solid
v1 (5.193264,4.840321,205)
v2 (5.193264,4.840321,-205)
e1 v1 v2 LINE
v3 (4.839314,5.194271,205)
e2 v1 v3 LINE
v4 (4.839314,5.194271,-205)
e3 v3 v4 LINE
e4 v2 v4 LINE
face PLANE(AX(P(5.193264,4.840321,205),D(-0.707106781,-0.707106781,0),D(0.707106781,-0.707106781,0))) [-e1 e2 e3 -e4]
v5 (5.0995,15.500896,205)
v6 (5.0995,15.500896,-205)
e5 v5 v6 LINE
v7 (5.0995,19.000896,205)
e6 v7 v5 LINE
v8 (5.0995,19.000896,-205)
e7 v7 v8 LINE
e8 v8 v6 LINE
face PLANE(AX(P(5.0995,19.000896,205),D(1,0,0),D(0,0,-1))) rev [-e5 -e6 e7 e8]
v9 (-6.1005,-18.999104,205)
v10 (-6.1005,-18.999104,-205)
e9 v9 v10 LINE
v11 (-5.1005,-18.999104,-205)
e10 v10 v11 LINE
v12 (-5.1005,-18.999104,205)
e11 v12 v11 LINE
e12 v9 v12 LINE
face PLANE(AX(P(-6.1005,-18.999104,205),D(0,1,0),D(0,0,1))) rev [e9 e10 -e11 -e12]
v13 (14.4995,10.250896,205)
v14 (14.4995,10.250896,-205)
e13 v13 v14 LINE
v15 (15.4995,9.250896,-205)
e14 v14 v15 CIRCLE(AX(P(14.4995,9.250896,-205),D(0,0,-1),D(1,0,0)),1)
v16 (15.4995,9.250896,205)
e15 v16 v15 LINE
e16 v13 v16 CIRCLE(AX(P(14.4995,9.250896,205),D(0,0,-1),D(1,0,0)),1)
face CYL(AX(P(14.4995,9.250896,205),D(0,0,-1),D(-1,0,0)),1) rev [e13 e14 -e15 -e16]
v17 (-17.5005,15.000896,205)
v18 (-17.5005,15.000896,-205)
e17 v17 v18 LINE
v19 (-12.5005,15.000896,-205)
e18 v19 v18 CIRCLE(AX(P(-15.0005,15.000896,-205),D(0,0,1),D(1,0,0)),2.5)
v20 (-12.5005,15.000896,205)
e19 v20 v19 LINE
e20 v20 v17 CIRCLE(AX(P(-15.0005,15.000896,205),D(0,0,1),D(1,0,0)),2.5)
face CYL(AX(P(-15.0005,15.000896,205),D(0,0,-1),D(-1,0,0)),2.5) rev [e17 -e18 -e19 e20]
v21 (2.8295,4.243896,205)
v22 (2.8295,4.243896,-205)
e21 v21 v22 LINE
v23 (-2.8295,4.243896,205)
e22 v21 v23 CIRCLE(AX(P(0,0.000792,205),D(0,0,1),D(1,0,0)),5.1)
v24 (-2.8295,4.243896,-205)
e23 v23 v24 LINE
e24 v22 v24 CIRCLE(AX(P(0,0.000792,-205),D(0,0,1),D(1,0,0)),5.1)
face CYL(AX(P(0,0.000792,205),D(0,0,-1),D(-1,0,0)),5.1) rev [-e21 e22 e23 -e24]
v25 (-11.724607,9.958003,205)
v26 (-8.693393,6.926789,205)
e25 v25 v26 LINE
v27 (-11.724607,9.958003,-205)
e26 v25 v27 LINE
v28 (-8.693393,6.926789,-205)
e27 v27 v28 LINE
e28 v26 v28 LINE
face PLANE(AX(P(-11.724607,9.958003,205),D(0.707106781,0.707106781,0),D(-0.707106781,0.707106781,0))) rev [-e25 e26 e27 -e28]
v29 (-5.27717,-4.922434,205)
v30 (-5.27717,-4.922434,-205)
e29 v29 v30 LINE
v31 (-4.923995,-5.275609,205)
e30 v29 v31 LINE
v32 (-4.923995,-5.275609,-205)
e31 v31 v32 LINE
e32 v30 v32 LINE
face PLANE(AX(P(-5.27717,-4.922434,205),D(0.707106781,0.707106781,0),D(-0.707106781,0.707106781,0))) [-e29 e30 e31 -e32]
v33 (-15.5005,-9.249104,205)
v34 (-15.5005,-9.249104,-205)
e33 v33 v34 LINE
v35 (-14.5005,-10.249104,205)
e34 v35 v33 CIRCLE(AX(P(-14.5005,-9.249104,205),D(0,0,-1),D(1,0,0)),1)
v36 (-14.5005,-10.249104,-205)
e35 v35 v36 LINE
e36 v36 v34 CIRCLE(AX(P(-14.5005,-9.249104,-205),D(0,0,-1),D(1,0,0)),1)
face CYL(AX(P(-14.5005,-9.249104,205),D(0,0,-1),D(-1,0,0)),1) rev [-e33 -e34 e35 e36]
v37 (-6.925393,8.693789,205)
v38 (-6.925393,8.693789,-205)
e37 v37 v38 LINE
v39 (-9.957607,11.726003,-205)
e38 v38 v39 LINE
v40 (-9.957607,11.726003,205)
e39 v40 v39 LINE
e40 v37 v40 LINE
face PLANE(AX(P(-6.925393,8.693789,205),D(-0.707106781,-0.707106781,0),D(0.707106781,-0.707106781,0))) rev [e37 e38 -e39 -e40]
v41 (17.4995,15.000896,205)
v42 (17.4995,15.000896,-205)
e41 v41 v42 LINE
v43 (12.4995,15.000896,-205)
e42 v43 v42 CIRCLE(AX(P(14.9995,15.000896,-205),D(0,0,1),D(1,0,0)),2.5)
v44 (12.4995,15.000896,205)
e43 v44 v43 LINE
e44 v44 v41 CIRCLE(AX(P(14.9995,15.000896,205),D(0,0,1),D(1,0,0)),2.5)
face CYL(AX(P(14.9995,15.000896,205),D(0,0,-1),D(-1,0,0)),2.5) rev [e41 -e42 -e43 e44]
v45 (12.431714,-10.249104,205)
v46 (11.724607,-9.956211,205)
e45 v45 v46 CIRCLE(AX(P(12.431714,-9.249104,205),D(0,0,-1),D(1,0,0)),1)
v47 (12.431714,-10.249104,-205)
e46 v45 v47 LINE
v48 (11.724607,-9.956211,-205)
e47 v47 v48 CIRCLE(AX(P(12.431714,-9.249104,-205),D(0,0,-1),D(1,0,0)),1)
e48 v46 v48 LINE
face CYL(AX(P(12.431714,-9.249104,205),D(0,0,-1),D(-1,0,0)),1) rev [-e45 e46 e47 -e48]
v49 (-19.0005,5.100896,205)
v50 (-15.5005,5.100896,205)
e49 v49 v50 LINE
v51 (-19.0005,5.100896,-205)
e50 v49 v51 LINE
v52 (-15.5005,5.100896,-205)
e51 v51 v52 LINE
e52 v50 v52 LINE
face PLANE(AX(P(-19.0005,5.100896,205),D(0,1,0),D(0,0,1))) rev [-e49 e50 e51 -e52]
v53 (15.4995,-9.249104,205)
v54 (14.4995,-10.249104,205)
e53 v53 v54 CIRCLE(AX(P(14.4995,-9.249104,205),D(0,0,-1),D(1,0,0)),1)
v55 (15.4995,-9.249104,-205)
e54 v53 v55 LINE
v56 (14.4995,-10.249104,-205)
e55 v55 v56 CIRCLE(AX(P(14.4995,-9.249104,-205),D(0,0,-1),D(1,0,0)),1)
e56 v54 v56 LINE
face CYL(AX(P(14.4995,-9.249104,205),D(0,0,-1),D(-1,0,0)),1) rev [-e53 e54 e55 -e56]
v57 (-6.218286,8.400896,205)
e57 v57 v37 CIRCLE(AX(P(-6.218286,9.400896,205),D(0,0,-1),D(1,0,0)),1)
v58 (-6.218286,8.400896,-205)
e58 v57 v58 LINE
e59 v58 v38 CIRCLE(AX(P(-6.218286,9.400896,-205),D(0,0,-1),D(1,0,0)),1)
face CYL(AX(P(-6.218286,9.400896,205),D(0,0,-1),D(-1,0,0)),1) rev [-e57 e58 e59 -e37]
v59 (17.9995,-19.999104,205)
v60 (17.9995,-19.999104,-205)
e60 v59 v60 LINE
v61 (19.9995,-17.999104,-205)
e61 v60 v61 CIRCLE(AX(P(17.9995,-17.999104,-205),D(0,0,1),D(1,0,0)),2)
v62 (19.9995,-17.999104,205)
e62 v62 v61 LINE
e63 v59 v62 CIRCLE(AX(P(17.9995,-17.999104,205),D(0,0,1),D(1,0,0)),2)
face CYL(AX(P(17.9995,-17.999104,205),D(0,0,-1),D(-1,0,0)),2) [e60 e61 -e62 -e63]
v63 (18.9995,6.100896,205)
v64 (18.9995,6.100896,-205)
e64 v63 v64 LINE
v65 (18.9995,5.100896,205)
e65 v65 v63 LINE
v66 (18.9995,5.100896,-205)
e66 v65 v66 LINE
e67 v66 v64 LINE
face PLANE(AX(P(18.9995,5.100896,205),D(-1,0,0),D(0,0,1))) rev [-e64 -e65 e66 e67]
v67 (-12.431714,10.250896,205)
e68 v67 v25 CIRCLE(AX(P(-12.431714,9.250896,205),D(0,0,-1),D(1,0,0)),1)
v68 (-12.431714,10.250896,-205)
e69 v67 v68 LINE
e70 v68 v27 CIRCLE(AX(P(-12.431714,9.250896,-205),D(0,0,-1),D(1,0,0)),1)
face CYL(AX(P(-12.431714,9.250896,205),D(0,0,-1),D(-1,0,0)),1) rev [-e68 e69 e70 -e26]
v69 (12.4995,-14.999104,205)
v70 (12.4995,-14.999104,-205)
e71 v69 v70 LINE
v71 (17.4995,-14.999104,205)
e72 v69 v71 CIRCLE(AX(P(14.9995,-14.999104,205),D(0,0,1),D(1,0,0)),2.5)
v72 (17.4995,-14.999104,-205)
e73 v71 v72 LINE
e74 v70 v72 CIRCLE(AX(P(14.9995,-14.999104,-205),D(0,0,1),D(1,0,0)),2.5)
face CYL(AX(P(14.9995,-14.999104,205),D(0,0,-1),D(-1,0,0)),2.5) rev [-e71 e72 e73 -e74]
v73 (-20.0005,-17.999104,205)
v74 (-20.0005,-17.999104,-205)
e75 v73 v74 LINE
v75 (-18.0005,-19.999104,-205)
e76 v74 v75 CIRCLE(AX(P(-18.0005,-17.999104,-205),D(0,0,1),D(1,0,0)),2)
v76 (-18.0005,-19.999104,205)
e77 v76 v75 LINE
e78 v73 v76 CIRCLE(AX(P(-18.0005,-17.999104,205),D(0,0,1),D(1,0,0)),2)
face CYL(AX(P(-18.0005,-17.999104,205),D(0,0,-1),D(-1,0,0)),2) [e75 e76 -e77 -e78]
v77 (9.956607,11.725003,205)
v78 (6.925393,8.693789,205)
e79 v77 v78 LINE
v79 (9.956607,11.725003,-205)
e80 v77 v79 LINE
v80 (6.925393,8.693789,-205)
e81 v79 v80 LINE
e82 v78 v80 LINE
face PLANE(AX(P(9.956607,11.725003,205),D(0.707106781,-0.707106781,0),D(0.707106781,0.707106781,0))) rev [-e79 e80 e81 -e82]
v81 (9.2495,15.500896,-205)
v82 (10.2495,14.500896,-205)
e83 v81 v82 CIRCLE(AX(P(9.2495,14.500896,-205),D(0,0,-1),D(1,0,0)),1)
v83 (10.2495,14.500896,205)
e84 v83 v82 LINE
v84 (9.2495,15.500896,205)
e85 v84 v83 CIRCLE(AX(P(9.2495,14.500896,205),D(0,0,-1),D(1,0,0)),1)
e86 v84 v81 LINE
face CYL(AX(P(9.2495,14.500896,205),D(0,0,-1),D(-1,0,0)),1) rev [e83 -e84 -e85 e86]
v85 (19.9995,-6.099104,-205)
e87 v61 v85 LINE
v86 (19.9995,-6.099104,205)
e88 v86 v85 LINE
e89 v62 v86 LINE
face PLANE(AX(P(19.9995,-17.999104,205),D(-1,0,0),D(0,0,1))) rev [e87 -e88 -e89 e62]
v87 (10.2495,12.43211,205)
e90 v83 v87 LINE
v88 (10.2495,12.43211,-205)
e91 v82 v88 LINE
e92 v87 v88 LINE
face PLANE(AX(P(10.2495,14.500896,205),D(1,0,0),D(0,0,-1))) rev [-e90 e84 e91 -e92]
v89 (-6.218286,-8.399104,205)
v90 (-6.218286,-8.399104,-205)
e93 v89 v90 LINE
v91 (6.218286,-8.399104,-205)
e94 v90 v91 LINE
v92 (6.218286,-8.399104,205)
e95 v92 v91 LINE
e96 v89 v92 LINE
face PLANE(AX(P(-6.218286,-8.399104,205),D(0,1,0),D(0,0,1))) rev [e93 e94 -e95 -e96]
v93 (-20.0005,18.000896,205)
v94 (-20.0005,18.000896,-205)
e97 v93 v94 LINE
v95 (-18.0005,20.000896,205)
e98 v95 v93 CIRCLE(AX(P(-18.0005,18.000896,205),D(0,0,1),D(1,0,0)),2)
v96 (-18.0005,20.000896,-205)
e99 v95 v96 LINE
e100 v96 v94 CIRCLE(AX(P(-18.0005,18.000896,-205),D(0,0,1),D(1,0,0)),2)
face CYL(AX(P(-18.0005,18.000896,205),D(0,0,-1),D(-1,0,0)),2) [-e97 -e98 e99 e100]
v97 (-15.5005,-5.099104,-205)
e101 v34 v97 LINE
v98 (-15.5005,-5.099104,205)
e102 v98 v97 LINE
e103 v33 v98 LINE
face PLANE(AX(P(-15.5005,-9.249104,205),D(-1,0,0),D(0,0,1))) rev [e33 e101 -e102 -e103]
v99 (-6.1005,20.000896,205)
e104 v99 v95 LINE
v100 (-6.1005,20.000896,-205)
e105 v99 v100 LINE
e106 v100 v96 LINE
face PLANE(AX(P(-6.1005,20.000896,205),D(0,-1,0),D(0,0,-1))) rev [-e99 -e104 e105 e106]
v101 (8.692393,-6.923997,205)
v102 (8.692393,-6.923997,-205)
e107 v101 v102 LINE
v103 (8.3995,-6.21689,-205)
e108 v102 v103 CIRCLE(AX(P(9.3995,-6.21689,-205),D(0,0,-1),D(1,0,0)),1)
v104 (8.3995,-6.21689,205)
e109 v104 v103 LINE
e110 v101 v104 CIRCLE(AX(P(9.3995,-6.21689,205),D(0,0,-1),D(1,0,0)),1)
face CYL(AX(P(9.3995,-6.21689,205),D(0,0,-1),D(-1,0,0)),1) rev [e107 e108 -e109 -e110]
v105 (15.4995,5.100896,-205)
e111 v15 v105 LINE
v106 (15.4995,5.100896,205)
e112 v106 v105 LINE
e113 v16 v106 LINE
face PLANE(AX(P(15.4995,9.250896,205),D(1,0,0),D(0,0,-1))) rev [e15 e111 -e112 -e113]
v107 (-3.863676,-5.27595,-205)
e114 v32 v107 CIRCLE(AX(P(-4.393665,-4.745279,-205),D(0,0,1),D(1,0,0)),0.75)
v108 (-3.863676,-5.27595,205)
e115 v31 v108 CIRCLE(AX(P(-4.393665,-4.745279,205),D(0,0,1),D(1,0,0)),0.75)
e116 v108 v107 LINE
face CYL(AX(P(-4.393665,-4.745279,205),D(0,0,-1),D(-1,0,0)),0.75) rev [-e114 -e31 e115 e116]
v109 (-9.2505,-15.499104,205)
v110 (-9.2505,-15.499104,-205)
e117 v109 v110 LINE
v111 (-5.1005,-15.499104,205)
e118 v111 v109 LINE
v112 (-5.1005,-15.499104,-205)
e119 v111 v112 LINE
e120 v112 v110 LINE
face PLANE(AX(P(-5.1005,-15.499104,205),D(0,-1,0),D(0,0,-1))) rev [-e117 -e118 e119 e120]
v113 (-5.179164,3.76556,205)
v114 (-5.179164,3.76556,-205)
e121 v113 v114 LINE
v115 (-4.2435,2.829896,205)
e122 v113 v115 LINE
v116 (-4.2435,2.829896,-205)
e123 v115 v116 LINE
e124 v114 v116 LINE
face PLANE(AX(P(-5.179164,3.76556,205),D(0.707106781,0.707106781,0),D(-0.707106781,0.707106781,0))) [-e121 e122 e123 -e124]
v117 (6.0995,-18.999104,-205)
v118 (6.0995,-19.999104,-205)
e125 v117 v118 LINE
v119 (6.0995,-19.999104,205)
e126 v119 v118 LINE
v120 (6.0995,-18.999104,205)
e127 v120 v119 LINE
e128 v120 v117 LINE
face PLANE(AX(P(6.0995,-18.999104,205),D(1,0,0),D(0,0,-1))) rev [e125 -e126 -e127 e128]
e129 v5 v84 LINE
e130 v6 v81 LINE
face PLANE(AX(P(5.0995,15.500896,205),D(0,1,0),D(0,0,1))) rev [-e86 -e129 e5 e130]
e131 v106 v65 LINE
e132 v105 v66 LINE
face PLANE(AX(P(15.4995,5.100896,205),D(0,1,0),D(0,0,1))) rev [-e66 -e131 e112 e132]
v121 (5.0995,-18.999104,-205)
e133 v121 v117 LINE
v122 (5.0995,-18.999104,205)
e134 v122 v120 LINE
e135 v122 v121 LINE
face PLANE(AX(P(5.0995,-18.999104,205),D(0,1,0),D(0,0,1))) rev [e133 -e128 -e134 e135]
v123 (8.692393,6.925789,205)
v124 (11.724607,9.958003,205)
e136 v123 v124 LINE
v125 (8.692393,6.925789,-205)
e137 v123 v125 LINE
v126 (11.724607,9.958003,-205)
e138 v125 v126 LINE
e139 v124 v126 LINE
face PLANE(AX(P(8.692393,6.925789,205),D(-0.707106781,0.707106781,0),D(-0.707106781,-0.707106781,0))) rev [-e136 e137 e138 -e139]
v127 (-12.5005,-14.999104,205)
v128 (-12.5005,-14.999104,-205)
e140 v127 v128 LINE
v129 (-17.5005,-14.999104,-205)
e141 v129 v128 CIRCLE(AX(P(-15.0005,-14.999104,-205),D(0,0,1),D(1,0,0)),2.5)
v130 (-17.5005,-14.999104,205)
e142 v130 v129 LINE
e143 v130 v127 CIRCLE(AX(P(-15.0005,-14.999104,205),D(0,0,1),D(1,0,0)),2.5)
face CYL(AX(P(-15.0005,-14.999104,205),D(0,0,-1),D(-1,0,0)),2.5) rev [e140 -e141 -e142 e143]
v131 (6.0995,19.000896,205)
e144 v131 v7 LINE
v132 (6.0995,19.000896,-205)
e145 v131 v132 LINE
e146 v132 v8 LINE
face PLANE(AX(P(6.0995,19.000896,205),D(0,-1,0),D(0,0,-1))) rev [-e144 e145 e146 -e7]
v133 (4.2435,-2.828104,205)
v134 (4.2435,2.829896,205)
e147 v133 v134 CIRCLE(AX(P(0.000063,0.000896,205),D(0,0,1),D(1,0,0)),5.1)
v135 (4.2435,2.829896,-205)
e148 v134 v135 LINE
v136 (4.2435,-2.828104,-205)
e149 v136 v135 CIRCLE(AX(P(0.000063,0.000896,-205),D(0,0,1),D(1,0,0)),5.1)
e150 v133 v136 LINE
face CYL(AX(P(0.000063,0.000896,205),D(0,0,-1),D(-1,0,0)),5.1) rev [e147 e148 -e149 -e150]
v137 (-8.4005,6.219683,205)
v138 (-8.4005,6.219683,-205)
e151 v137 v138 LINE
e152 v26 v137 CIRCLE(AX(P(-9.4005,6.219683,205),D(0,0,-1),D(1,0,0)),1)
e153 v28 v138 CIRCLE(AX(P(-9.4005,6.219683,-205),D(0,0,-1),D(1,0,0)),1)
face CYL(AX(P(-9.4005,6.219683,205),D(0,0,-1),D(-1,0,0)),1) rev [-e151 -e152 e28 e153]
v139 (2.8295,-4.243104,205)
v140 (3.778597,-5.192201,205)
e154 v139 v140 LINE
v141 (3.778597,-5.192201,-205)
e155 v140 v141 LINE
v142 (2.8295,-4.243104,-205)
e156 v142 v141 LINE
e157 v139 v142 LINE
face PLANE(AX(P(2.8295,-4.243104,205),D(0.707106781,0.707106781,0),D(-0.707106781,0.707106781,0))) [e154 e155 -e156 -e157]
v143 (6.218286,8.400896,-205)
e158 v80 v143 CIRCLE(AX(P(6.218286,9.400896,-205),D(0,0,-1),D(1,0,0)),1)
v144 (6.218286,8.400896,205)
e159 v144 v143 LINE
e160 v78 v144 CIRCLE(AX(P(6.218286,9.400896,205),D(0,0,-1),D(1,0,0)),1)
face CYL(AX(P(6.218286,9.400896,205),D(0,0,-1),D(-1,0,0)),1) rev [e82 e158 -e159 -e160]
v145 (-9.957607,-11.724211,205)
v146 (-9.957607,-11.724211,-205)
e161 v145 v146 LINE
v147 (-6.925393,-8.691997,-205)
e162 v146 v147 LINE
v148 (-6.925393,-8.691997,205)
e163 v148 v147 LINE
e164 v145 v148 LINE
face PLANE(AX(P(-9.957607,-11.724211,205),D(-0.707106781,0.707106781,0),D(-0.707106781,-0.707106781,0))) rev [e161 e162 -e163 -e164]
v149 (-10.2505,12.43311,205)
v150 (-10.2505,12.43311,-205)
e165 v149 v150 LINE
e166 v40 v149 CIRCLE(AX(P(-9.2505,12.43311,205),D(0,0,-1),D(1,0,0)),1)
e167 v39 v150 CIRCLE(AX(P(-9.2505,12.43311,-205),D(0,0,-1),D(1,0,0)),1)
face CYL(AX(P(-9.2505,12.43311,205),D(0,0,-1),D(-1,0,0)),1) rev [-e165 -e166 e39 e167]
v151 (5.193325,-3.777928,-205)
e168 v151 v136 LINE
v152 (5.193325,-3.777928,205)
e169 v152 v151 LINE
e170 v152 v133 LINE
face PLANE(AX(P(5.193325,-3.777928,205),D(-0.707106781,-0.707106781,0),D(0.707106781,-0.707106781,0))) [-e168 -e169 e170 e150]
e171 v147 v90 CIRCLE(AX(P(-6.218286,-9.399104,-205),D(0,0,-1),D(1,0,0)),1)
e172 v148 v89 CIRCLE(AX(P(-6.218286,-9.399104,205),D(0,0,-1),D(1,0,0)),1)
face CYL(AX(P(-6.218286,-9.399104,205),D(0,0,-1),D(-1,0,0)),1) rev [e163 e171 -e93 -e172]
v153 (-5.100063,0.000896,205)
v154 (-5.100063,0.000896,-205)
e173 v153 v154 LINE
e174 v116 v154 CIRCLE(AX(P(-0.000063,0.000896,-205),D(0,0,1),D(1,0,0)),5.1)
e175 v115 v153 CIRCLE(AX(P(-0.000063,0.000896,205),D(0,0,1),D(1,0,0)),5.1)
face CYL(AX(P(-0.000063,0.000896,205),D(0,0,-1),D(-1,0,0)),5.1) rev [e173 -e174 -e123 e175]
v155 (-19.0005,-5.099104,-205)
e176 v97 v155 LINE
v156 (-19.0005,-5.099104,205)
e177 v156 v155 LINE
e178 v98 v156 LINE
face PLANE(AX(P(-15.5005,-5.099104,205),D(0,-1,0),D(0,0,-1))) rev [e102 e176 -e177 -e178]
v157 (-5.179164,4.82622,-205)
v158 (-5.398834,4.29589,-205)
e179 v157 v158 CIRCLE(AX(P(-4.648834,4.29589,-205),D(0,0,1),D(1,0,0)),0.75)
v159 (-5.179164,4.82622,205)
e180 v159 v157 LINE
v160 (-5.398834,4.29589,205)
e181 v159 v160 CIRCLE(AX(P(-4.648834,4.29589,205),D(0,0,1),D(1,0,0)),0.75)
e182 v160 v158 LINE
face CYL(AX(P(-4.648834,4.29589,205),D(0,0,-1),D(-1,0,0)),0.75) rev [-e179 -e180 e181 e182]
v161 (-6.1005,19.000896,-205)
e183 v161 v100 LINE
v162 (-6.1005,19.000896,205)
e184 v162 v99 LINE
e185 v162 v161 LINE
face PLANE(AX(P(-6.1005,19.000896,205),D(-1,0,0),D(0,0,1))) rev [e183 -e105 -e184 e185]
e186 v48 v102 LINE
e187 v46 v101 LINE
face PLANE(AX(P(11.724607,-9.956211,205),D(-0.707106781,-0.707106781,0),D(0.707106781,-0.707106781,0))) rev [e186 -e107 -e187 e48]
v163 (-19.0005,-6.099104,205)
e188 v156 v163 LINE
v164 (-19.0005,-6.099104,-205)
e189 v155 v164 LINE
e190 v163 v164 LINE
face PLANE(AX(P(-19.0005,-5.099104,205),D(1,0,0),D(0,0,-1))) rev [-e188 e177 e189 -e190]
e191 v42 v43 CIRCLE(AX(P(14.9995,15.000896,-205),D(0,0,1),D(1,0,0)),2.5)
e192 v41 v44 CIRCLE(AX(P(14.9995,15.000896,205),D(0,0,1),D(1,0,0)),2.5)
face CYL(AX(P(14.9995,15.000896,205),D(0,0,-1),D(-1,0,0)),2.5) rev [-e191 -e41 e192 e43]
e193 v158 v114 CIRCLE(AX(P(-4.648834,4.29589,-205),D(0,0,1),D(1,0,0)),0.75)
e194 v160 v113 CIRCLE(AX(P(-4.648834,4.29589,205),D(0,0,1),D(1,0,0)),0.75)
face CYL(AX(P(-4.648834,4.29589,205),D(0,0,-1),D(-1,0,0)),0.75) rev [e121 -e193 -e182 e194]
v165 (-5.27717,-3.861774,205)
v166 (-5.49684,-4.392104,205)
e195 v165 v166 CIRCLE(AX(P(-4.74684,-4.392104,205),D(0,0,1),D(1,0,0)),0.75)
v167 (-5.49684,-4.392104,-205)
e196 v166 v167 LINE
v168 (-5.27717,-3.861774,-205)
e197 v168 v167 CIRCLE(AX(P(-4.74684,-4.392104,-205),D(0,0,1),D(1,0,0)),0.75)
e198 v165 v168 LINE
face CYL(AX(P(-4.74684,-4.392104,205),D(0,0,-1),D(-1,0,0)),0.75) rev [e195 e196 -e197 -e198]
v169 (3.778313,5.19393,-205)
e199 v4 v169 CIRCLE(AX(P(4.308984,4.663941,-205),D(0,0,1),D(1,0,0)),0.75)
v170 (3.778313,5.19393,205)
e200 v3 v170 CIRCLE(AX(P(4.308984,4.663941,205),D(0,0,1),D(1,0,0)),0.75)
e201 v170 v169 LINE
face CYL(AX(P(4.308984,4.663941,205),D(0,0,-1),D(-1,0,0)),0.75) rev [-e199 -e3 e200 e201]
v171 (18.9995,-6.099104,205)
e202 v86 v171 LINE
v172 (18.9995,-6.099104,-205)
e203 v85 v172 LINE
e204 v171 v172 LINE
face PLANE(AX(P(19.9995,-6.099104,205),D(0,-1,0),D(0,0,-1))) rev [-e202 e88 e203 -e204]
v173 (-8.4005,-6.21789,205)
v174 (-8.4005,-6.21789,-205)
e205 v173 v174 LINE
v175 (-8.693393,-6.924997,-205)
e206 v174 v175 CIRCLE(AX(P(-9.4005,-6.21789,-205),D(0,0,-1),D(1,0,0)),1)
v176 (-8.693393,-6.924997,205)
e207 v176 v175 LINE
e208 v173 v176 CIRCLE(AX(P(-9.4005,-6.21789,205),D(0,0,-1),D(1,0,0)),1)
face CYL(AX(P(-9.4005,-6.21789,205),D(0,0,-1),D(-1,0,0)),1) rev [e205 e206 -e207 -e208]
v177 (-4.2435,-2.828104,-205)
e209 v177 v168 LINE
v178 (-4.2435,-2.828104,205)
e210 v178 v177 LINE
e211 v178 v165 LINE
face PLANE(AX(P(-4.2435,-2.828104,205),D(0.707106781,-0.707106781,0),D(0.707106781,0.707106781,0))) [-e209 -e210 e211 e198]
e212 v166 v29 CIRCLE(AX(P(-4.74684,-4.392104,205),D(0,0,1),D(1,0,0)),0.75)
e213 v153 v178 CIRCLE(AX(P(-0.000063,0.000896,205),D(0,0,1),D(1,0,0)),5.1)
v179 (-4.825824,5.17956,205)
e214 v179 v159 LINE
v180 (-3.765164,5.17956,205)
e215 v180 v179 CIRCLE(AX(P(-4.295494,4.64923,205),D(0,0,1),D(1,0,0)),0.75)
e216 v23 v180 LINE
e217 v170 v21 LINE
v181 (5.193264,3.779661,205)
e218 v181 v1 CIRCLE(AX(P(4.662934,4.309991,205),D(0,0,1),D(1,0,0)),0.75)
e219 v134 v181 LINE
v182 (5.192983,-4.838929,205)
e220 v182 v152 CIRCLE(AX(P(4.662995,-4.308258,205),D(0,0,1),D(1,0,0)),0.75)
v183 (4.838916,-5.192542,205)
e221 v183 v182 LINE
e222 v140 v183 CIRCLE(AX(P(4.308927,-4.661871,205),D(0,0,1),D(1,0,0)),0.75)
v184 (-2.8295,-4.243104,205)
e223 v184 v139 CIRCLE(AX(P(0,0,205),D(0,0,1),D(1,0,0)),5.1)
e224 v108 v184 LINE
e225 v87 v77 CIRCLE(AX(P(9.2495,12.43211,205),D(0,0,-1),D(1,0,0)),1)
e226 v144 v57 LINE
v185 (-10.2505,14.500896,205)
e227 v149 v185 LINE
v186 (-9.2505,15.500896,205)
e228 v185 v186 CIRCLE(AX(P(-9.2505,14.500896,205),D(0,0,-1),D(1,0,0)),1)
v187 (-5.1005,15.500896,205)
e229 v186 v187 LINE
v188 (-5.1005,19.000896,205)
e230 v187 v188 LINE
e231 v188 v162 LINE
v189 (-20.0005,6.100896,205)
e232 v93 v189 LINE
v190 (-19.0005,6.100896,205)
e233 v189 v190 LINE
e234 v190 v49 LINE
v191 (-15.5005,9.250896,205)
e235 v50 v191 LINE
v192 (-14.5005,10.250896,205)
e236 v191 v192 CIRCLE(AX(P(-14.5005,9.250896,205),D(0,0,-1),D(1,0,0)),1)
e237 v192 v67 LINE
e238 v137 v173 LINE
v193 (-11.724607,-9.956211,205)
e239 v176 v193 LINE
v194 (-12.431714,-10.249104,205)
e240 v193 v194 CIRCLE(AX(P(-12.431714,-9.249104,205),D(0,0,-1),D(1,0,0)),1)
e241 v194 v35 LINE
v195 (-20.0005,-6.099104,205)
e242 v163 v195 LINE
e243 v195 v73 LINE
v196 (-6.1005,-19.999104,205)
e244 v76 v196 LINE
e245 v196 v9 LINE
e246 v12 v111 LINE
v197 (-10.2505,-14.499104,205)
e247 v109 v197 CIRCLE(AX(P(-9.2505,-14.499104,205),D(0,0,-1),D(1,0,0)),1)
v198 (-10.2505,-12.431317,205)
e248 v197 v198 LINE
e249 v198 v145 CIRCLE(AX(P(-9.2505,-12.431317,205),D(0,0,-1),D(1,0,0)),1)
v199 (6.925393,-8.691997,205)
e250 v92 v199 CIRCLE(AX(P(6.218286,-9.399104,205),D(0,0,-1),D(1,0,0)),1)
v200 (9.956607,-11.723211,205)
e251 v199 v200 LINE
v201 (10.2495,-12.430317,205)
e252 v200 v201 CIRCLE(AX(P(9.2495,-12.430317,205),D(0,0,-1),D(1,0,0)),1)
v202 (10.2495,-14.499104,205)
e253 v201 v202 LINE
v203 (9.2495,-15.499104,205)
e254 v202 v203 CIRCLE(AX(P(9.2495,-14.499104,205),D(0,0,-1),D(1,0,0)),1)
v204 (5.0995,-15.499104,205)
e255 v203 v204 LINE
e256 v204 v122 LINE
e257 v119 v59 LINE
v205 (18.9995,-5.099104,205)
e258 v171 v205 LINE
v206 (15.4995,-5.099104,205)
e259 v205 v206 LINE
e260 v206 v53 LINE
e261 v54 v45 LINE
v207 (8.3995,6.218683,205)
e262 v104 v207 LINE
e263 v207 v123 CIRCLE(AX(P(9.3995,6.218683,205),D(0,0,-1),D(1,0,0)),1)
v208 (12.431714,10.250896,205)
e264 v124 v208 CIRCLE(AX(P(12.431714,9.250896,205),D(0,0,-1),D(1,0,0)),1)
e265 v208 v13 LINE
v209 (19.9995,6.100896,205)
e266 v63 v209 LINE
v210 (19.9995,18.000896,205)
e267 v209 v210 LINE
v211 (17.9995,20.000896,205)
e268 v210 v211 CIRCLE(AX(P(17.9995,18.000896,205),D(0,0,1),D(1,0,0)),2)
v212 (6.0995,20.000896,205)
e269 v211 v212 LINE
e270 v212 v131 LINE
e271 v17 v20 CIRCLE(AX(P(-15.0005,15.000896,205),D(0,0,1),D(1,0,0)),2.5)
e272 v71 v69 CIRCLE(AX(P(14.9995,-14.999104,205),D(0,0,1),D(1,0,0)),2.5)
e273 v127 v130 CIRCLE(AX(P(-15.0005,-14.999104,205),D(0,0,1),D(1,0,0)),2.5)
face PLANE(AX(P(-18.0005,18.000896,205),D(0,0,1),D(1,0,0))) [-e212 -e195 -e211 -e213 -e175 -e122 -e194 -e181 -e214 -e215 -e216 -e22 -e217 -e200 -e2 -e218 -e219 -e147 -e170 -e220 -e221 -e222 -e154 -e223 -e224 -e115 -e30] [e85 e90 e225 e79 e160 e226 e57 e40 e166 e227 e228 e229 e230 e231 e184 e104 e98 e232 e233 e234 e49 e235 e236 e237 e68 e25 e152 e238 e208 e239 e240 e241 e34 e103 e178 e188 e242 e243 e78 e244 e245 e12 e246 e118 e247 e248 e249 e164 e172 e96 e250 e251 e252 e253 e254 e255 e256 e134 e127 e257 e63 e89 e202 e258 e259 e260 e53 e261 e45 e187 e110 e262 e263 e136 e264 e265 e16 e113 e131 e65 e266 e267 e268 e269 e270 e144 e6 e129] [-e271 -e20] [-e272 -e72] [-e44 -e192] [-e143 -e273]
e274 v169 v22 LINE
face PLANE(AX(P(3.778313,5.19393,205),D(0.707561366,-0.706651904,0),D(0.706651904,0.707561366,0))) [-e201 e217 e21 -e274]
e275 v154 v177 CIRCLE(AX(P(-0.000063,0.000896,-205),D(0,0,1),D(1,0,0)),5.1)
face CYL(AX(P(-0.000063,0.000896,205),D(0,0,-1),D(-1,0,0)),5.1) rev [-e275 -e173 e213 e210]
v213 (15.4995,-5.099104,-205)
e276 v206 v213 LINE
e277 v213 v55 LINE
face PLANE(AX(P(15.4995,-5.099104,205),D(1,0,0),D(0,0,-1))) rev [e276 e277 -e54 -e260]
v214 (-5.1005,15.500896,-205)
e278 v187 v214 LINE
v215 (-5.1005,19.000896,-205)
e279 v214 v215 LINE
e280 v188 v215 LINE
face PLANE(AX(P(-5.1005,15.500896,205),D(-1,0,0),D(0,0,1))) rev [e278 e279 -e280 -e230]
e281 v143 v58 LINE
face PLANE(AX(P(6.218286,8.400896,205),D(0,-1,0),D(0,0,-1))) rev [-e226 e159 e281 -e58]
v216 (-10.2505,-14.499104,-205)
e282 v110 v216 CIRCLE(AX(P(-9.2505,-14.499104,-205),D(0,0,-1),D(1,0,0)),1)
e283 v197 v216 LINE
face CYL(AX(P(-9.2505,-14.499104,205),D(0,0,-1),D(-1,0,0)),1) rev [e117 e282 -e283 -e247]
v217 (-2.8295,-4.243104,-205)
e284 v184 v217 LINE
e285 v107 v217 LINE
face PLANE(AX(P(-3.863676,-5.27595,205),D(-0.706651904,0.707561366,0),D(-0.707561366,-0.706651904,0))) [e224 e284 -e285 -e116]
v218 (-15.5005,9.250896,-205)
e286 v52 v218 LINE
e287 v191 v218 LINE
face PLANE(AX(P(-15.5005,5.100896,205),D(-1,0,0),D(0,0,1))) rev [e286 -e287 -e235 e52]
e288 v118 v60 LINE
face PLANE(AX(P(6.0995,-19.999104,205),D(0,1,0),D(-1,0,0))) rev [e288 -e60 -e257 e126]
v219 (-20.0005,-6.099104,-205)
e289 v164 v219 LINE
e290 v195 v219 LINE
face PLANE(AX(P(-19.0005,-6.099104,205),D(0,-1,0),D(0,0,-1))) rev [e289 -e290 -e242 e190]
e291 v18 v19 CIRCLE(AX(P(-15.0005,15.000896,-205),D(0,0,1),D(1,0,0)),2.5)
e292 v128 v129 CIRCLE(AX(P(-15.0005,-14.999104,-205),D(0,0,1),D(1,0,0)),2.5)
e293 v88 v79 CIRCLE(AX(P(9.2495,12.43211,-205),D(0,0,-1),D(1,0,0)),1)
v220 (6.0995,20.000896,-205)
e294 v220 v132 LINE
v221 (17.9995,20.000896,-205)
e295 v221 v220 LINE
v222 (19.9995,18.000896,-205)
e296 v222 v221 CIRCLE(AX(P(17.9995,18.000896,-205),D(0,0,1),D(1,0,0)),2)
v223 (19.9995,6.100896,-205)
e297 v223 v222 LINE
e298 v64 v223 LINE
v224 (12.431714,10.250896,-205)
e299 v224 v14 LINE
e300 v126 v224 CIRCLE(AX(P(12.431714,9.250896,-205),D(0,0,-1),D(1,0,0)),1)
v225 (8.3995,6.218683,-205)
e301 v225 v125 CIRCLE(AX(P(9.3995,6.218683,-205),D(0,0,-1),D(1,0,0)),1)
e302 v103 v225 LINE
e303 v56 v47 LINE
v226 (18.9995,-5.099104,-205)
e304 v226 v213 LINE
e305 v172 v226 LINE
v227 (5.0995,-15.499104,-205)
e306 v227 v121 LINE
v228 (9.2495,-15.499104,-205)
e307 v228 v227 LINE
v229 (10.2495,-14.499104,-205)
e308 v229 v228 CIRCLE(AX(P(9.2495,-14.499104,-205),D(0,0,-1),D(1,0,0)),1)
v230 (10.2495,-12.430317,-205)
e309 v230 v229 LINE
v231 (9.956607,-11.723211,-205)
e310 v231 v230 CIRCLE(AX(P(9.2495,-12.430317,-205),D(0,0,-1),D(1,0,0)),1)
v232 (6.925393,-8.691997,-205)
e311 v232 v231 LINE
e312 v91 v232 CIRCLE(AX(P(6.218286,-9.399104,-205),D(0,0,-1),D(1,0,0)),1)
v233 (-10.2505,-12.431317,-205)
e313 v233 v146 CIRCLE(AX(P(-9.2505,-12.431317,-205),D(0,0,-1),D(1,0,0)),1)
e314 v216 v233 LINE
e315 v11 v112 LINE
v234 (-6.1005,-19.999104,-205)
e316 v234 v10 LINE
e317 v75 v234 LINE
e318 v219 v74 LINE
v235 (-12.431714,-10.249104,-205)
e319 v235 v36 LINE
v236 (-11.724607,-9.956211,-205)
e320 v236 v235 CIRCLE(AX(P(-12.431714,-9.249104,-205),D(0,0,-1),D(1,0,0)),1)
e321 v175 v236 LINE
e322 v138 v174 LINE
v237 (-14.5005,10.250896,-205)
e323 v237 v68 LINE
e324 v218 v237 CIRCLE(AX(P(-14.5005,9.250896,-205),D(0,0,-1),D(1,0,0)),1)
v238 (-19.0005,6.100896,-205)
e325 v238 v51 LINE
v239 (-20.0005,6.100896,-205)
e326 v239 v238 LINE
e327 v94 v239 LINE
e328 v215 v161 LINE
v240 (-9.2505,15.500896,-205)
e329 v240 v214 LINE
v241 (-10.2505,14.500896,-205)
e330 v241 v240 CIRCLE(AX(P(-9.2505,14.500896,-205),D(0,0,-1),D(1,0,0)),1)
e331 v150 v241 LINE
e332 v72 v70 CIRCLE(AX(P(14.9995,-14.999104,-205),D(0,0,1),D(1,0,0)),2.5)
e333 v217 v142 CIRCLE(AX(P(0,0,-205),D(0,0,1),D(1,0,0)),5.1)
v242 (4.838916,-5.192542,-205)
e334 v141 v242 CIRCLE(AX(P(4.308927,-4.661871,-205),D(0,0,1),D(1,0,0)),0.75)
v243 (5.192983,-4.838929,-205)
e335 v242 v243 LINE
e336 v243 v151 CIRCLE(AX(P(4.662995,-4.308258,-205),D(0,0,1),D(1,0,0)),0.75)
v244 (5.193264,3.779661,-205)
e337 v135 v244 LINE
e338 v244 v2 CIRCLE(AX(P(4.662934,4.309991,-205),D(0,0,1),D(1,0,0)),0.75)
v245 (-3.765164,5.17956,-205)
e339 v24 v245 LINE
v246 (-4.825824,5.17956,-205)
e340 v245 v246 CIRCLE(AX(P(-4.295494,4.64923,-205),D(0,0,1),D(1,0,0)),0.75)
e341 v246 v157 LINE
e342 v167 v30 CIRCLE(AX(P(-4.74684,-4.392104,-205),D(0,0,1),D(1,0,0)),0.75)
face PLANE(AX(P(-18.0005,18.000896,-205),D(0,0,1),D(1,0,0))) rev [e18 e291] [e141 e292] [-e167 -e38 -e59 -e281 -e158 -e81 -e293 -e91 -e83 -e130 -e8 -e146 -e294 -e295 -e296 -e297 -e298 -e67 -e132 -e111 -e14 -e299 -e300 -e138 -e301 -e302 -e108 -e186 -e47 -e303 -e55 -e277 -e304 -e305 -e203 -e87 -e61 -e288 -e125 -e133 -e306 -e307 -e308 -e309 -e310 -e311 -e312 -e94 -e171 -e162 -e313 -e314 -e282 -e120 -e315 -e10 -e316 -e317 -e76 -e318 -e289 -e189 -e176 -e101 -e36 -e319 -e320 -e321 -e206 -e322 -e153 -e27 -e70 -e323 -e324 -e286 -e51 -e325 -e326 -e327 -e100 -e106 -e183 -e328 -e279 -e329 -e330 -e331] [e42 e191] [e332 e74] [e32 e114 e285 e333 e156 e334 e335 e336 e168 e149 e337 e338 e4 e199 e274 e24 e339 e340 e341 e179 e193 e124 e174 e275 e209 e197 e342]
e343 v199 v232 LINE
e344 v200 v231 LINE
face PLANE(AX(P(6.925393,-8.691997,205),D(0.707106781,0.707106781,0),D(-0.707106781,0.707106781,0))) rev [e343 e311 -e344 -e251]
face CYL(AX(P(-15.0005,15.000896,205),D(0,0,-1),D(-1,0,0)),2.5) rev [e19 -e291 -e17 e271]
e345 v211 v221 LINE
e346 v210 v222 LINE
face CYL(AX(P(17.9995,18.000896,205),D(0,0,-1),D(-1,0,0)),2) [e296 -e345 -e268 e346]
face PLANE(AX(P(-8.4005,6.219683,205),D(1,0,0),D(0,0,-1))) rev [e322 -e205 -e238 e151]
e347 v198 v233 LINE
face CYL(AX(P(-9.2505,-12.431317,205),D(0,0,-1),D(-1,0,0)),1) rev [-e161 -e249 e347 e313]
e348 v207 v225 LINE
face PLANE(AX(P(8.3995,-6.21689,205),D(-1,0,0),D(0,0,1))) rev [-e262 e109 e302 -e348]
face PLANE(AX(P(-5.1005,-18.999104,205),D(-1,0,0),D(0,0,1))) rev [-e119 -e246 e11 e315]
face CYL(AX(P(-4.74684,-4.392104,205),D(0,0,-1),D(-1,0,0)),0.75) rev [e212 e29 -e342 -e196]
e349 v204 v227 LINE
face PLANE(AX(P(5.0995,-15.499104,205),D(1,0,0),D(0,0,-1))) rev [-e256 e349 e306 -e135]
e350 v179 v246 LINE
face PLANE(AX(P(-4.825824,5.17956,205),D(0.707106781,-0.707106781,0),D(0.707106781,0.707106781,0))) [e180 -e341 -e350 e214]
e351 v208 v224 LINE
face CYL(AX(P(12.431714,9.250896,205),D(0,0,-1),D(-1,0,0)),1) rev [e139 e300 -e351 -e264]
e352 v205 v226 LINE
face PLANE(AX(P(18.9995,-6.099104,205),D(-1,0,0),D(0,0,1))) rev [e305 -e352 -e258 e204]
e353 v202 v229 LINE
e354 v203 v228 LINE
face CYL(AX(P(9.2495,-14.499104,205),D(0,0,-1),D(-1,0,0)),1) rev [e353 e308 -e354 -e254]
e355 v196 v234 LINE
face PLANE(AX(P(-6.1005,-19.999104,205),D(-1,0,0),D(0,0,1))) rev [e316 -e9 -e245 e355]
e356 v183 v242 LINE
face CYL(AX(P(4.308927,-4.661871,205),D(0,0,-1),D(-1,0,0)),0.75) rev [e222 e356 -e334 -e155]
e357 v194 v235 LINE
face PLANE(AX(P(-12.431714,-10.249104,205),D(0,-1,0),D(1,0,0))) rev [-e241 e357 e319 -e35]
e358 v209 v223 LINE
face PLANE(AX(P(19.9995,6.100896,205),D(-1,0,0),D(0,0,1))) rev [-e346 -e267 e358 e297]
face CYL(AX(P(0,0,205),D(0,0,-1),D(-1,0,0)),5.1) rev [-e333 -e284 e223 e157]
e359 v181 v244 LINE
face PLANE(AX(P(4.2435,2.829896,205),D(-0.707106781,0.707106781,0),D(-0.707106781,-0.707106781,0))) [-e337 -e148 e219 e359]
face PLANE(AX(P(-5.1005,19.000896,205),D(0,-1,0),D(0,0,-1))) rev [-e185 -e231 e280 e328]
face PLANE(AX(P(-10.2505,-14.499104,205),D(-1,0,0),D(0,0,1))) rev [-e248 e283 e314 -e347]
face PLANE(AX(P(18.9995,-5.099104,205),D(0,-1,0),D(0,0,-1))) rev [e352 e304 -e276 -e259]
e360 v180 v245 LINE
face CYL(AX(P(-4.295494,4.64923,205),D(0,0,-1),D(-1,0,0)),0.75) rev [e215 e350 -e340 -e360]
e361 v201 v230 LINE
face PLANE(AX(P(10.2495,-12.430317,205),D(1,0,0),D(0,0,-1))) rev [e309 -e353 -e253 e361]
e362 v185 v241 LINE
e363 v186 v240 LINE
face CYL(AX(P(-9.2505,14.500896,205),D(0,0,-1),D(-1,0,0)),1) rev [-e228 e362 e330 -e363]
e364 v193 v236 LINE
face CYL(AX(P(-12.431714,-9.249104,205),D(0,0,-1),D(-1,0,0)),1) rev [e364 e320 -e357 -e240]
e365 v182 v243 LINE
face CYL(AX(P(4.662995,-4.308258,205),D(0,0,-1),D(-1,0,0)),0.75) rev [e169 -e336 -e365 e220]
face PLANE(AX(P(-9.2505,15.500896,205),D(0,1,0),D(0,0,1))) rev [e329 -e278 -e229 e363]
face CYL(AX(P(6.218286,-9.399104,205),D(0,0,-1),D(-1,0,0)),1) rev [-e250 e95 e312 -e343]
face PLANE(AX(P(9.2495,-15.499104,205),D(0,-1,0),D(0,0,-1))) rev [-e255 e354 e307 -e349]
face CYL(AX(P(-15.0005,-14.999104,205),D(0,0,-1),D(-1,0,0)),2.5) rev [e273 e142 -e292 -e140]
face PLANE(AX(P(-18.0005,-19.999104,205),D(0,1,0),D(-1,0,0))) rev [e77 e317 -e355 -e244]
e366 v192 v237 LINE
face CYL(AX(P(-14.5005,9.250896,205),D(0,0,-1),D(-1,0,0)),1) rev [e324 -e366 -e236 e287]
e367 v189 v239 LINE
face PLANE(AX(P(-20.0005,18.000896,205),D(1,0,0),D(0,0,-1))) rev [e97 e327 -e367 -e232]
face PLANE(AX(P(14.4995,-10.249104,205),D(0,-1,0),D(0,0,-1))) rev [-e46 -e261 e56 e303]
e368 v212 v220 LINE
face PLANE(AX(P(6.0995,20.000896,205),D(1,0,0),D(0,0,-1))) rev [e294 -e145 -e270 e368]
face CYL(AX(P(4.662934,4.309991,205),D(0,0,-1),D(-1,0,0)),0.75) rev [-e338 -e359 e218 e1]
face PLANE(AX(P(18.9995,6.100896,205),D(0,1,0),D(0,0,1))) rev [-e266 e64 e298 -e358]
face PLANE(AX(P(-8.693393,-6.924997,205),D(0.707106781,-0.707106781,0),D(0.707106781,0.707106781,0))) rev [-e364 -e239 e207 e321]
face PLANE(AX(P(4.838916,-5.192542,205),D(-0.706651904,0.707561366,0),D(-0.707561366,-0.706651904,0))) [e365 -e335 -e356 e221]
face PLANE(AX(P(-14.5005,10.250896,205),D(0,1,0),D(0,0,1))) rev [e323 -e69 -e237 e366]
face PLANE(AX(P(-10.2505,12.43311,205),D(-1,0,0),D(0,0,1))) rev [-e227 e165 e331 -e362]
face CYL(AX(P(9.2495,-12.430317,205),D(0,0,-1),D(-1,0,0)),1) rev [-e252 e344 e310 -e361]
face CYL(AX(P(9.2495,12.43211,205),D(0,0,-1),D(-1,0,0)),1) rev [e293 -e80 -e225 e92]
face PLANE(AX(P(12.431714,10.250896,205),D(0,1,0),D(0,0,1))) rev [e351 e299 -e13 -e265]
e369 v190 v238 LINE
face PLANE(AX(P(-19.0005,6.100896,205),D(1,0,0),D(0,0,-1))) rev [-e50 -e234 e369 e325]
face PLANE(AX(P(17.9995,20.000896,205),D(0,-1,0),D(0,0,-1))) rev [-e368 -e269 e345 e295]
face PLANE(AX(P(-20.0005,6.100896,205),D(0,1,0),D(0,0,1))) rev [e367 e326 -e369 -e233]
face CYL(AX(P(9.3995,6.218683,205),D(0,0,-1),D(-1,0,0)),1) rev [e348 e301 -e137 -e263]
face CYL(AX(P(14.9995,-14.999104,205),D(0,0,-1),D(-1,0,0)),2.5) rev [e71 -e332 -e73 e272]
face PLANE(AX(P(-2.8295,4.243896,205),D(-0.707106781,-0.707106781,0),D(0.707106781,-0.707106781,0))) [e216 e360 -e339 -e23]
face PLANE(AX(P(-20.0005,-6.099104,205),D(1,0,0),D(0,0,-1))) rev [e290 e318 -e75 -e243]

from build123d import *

# Parameters (mm, degrees)
SKETCH1_R           = 2.5
BOSS_EXTRUDE1_DEPTH = 205


with BuildPart() as part:
    # Sketch1 → Boss-Extrude1 (new, symmetric)
    with BuildSketch(Plane.XY):
        with BuildLine():
            Line((-5.1005, 15.500896213), (-5.1005, 19.000896213))
            Line((-5.1005, 19.000896213), (-6.1005, 19.000896213))
            Line((-6.1005, 19.000896213), (-6.1005, 20.000896213))
            Line((-6.1005, 20.000896213), (-18.0005, 20.000896213))
            ThreePointArc((-18.0005, 20.000896213), (-19.414713562, 19.415109775), (-20.0005, 18.000896213))
            Line((-20.0005, 18.000896213), (-20.0005, 6.100896213))
            Line((-20.0005, 6.100896213), (-19.0005, 6.100896213))
            Line((-19.0005, 6.100896213), (-19.0005, 5.100896213))
            Line((-19.0005, 5.100896213), (-15.5005, 5.100896213))
            Line((-15.5005, 5.100896213), (-15.5005, 9.250896213))
            ThreePointArc((-15.5005, 9.250896213), (-15.207606781, 9.958002994), (-14.5005, 10.250896213))
            Line((-14.5005, 10.250896213), (-12.431713562, 10.250896213))
            ThreePointArc((-12.431713562, 10.250896213), (-12.049030228, 10.174775786), (-11.724606932, 9.958003144))
            Line((-11.724606932, 9.958003144), (-8.693393219, 6.926789431))
            ThreePointArc((-8.693393219, 6.926789431), (-8.476620546, 6.602366272), (-8.4005, 6.21968306))
            Line((-8.4005, 6.21968306), (-8.4005, -6.217890225))
            ThreePointArc((-8.4005, -6.217890225), (-8.476620502, -6.60057374), (-8.693393346, -6.924997133))
            Line((-8.693393346, -6.924997133), (-11.724606781, -9.956210569))
            ThreePointArc((-11.724606781, -9.956210569), (-12.049030198, -10.172983348), (-12.431713709, -10.249103787))
            Line((-12.431713709, -10.249103787), (-14.5005, -10.249103787))
            ThreePointArc((-14.5005, -10.249103787), (-15.207606781, -9.956210569), (-15.5005, -9.249103787))
            Line((-15.5005, -9.249103787), (-15.5005, -5.099103787))
            Line((-15.5005, -5.099103787), (-19.0005, -5.099103787))
            Line((-19.0005, -5.099103787), (-19.0005, -6.099103787))
            Line((-19.0005, -6.099103787), (-20.0005, -6.099103787))
            Line((-20.0005, -6.099103787), (-20.0005, -17.999103787))
            ThreePointArc((-20.0005, -17.999103787), (-19.414713562, -19.41331735), (-18.0005, -19.999103787))
            Line((-18.0005, -19.999103787), (-6.1005, -19.999103787))
            Line((-6.1005, -19.999103787), (-6.1005, -18.999103787))
            Line((-6.1005, -18.999103787), (-5.1005, -18.999103787))
            Line((-5.1005, -18.999103787), (-5.1005, -15.499103787))
            Line((-5.1005, -15.499103787), (-9.2505, -15.499103787))
            ThreePointArc((-9.2505, -15.499103787), (-9.957606781, -15.206210569), (-10.2505, -14.499103787))
            Line((-10.2505, -14.499103787), (-10.2505, -12.43131735))
            ThreePointArc((-10.2505, -12.43131735), (-10.174379535, -12.048633922), (-9.957606789, -11.724210576))
            Line((-9.957606789, -11.724210576), (-6.925393219, -8.691997006))
            ThreePointArc((-6.925393219, -8.691997006), (-6.60096987, -8.475224255), (-6.218286438, -8.399103787))
            Line((-6.218286438, -8.399103787), (6.218286438, -8.399103787))
            ThreePointArc((6.218286438, -8.399103787), (6.600969772, -8.475224214), (6.925393068, -8.691996856))
            Line((6.925393068, -8.691996856), (9.956606781, -11.723210569))
            ThreePointArc((9.956606781, -11.723210569), (10.173379454, -12.047633728), (10.2495, -12.43031694))
            Line((10.2495, -12.43031694), (10.2495, -14.499103787))
            ThreePointArc((10.2495, -14.499103787), (9.956606781, -15.206210569), (9.2495, -15.499103787))
            Line((9.2495, -15.499103787), (5.0995, -15.499103787))
            Line((5.0995, -15.499103787), (5.0995, -18.999103787))
            Line((5.0995, -18.999103787), (6.0995, -18.999103787))
            Line((6.0995, -18.999103787), (6.0995, -19.999103787))
            Line((6.0995, -19.999103787), (17.9995, -19.999103787))
            ThreePointArc((17.9995, -19.999103787), (19.413713562, -19.41331735), (19.9995, -17.999103787))
            Line((19.9995, -17.999103787), (19.9995, -6.099103787))
            Line((19.9995, -6.099103787), (18.9995, -6.099103787))
            Line((18.9995, -6.099103787), (18.9995, -5.099103787))
            Line((18.9995, -5.099103787), (15.4995, -5.099103787))
            Line((15.4995, -5.099103787), (15.4995, -9.249103787))
            ThreePointArc((15.4995, -9.249103787), (15.206606781, -9.956210569), (14.4995, -10.249103787))
            Line((14.4995, -10.249103787), (12.431713562, -10.249103787))
            ThreePointArc((12.431713562, -10.249103787), (12.049030135, -10.172983322), (11.724606789, -9.956210576))
            Line((11.724606789, -9.956210576), (8.692393219, -6.923997006))
            ThreePointArc((8.692393219, -6.923997006), (8.475620467, -6.599573657), (8.3995, -6.216890225))
            Line((8.3995, -6.216890225), (8.3995, 6.21868265))
            ThreePointArc((8.3995, 6.21868265), (8.475620465, 6.601366078), (8.692393211, 6.925789424))
            Line((8.692393211, 6.925789424), (11.724606781, 9.958002994))
            ThreePointArc((11.724606781, 9.958002994), (12.04903013, 10.174775745), (12.431713562, 10.250896213))
            Line((12.431713562, 10.250896213), (14.4995, 10.250896213))
            ThreePointArc((14.4995, 10.250896213), (15.206606781, 9.958002994), (15.4995, 9.250896213))
            Line((15.4995, 9.250896213), (15.4995, 5.100896213))
            Line((15.4995, 5.100896213), (18.9995, 5.100896213))
            Line((18.9995, 5.100896213), (18.9995, 6.100896213))
            Line((18.9995, 6.100896213), (19.9995, 6.100896213))
            Line((19.9995, 6.100896213), (19.9995, 18.000896213))
            ThreePointArc((19.9995, 18.000896213), (19.413713562, 19.415109775), (17.9995, 20.000896213))
            Line((17.9995, 20.000896213), (6.0995, 20.000896213))
            Line((6.0995, 20.000896213), (6.0995, 19.000896213))
            Line((6.0995, 19.000896213), (5.0995, 19.000896213))
            Line((5.0995, 19.000896213), (5.0995, 15.500896213))
            Line((5.0995, 15.500896213), (9.2495, 15.500896213))
            ThreePointArc((9.2495, 15.500896213), (9.956606781, 15.208002994), (10.2495, 14.500896213))
            Line((10.2495, 14.500896213), (10.2495, 12.432109775))
            ThreePointArc((10.2495, 12.432109775), (10.173379498, 12.04942626), (9.956606654, 11.725002867))
            Line((9.956606654, 11.725002867), (6.925393219, 8.693789431))
            ThreePointArc((6.925393219, 8.693789431), (6.600969802, 8.477016652), (6.218286291, 8.400896213))
            Line((6.218286291, 8.400896213), (-6.218286438, 8.400896213))
            ThreePointArc((-6.218286438, 8.400896213), (-6.600969865, 8.477016678), (-6.925393211, 8.693789424))
            Line((-6.925393211, 8.693789424), (-9.957606781, 11.726002994))
            ThreePointArc((-9.957606781, 11.726002994), (-10.174379533, 12.050426343), (-10.2505, 12.433109775))
            Line((-10.2505, 12.433109775), (-10.2505, 14.500896213))
            ThreePointArc((-10.2505, 14.500896213), (-9.957606781, 15.208002994), (-9.2505, 15.500896213))
            Line((-9.2505, 15.500896213), (-5.1005, 15.500896213))
        make_face()
        with Locations((-15.0005, 15.000896213)):
            Circle(SKETCH1_R, mode=Mode.SUBTRACT)
        with Locations((14.9995, -14.999103787)):
            Circle(SKETCH1_R, mode=Mode.SUBTRACT)
        with Locations((-15.0005, -14.999103787)):
            Circle(SKETCH1_R, mode=Mode.SUBTRACT)
        with Locations((14.9995, 15.000896213)):
            Circle(SKETCH1_R, mode=Mode.SUBTRACT)
        with BuildLine():
            Line((-5.179163629, 3.765559841), (-4.2435, 2.829896213))
            ThreePointArc((-4.2435, 2.829896213), (-5.100062832, 0.000896213), (-4.2435, -2.828103787))
            Line((-4.2435, -2.828103787), (-5.277169914, -3.861773701))
            ThreePointArc((-5.277169914, -3.861773701), (-5.496839828, -4.392103787), (-5.277169914, -4.922433873))
            Line((-5.277169914, -4.922433873), (-4.923994614, -5.275609174))
            ThreePointArc((-4.923994614, -5.275609174), (-4.393905685, -5.495279049), (-3.8636756, -5.275950112))
            Line((-3.8636756, -5.275950112), (-2.8295, -4.243103787))
            ThreePointArc((-2.8295, -4.243103787), (0, -5.1), (2.8295, -4.243103787))
            Line((2.8295, -4.243103787), (3.778597046, -5.192200834))
            ThreePointArc((3.778597046, -5.192200834), (4.308685975, -5.411870709), (4.83891606, -5.192541772))
            Line((4.83891606, -5.192541772), (5.192983438, -4.838929494))
            ThreePointArc((5.192983438, -4.838929494), (5.412994471, -4.308499627), (5.193324596, -3.777928383))
            Line((5.193324596, -3.777928383), (4.2435, -2.828103787))
            ThreePointArc((4.2435, -2.828103787), (5.100062832, 0.000896213), (4.2435, 2.829896213))
            Line((4.2435, 2.829896213), (5.193264407, 3.77966062))
            ThreePointArc((5.193264407, 3.77966062), (5.412934321, 4.309990706), (5.193264407, 4.840320791))
            Line((5.193264407, 4.840320791), (4.839313907, 5.194271291))
            ThreePointArc((4.839313907, 5.194271291), (4.308742664, 5.413941166), (3.778312797, 5.193930133))
            Line((3.778312797, 5.193930133), (2.8295, 4.243896213))
            ThreePointArc((2.8295, 4.243896213), (0, 5.100792425), (-2.8295, 4.243896213))
            Line((-2.8295, 4.243896213), (-3.765163629, 5.179559841))
            ThreePointArc((-3.765163629, 5.179559841), (-4.295493715, 5.399229756), (-4.825823801, 5.179559841))
            Line((-4.825823801, 5.179559841), (-5.179163629, 4.826220013))
            ThreePointArc((-5.179163629, 4.826220013), (-5.398833543, 4.295889927), (-5.179163629, 3.765559841))
        make_face(mode=Mode.SUBTRACT)
    extrude(amount=BOSS_EXTRUDE1_DEPTH, both=True)


solid = part.part
